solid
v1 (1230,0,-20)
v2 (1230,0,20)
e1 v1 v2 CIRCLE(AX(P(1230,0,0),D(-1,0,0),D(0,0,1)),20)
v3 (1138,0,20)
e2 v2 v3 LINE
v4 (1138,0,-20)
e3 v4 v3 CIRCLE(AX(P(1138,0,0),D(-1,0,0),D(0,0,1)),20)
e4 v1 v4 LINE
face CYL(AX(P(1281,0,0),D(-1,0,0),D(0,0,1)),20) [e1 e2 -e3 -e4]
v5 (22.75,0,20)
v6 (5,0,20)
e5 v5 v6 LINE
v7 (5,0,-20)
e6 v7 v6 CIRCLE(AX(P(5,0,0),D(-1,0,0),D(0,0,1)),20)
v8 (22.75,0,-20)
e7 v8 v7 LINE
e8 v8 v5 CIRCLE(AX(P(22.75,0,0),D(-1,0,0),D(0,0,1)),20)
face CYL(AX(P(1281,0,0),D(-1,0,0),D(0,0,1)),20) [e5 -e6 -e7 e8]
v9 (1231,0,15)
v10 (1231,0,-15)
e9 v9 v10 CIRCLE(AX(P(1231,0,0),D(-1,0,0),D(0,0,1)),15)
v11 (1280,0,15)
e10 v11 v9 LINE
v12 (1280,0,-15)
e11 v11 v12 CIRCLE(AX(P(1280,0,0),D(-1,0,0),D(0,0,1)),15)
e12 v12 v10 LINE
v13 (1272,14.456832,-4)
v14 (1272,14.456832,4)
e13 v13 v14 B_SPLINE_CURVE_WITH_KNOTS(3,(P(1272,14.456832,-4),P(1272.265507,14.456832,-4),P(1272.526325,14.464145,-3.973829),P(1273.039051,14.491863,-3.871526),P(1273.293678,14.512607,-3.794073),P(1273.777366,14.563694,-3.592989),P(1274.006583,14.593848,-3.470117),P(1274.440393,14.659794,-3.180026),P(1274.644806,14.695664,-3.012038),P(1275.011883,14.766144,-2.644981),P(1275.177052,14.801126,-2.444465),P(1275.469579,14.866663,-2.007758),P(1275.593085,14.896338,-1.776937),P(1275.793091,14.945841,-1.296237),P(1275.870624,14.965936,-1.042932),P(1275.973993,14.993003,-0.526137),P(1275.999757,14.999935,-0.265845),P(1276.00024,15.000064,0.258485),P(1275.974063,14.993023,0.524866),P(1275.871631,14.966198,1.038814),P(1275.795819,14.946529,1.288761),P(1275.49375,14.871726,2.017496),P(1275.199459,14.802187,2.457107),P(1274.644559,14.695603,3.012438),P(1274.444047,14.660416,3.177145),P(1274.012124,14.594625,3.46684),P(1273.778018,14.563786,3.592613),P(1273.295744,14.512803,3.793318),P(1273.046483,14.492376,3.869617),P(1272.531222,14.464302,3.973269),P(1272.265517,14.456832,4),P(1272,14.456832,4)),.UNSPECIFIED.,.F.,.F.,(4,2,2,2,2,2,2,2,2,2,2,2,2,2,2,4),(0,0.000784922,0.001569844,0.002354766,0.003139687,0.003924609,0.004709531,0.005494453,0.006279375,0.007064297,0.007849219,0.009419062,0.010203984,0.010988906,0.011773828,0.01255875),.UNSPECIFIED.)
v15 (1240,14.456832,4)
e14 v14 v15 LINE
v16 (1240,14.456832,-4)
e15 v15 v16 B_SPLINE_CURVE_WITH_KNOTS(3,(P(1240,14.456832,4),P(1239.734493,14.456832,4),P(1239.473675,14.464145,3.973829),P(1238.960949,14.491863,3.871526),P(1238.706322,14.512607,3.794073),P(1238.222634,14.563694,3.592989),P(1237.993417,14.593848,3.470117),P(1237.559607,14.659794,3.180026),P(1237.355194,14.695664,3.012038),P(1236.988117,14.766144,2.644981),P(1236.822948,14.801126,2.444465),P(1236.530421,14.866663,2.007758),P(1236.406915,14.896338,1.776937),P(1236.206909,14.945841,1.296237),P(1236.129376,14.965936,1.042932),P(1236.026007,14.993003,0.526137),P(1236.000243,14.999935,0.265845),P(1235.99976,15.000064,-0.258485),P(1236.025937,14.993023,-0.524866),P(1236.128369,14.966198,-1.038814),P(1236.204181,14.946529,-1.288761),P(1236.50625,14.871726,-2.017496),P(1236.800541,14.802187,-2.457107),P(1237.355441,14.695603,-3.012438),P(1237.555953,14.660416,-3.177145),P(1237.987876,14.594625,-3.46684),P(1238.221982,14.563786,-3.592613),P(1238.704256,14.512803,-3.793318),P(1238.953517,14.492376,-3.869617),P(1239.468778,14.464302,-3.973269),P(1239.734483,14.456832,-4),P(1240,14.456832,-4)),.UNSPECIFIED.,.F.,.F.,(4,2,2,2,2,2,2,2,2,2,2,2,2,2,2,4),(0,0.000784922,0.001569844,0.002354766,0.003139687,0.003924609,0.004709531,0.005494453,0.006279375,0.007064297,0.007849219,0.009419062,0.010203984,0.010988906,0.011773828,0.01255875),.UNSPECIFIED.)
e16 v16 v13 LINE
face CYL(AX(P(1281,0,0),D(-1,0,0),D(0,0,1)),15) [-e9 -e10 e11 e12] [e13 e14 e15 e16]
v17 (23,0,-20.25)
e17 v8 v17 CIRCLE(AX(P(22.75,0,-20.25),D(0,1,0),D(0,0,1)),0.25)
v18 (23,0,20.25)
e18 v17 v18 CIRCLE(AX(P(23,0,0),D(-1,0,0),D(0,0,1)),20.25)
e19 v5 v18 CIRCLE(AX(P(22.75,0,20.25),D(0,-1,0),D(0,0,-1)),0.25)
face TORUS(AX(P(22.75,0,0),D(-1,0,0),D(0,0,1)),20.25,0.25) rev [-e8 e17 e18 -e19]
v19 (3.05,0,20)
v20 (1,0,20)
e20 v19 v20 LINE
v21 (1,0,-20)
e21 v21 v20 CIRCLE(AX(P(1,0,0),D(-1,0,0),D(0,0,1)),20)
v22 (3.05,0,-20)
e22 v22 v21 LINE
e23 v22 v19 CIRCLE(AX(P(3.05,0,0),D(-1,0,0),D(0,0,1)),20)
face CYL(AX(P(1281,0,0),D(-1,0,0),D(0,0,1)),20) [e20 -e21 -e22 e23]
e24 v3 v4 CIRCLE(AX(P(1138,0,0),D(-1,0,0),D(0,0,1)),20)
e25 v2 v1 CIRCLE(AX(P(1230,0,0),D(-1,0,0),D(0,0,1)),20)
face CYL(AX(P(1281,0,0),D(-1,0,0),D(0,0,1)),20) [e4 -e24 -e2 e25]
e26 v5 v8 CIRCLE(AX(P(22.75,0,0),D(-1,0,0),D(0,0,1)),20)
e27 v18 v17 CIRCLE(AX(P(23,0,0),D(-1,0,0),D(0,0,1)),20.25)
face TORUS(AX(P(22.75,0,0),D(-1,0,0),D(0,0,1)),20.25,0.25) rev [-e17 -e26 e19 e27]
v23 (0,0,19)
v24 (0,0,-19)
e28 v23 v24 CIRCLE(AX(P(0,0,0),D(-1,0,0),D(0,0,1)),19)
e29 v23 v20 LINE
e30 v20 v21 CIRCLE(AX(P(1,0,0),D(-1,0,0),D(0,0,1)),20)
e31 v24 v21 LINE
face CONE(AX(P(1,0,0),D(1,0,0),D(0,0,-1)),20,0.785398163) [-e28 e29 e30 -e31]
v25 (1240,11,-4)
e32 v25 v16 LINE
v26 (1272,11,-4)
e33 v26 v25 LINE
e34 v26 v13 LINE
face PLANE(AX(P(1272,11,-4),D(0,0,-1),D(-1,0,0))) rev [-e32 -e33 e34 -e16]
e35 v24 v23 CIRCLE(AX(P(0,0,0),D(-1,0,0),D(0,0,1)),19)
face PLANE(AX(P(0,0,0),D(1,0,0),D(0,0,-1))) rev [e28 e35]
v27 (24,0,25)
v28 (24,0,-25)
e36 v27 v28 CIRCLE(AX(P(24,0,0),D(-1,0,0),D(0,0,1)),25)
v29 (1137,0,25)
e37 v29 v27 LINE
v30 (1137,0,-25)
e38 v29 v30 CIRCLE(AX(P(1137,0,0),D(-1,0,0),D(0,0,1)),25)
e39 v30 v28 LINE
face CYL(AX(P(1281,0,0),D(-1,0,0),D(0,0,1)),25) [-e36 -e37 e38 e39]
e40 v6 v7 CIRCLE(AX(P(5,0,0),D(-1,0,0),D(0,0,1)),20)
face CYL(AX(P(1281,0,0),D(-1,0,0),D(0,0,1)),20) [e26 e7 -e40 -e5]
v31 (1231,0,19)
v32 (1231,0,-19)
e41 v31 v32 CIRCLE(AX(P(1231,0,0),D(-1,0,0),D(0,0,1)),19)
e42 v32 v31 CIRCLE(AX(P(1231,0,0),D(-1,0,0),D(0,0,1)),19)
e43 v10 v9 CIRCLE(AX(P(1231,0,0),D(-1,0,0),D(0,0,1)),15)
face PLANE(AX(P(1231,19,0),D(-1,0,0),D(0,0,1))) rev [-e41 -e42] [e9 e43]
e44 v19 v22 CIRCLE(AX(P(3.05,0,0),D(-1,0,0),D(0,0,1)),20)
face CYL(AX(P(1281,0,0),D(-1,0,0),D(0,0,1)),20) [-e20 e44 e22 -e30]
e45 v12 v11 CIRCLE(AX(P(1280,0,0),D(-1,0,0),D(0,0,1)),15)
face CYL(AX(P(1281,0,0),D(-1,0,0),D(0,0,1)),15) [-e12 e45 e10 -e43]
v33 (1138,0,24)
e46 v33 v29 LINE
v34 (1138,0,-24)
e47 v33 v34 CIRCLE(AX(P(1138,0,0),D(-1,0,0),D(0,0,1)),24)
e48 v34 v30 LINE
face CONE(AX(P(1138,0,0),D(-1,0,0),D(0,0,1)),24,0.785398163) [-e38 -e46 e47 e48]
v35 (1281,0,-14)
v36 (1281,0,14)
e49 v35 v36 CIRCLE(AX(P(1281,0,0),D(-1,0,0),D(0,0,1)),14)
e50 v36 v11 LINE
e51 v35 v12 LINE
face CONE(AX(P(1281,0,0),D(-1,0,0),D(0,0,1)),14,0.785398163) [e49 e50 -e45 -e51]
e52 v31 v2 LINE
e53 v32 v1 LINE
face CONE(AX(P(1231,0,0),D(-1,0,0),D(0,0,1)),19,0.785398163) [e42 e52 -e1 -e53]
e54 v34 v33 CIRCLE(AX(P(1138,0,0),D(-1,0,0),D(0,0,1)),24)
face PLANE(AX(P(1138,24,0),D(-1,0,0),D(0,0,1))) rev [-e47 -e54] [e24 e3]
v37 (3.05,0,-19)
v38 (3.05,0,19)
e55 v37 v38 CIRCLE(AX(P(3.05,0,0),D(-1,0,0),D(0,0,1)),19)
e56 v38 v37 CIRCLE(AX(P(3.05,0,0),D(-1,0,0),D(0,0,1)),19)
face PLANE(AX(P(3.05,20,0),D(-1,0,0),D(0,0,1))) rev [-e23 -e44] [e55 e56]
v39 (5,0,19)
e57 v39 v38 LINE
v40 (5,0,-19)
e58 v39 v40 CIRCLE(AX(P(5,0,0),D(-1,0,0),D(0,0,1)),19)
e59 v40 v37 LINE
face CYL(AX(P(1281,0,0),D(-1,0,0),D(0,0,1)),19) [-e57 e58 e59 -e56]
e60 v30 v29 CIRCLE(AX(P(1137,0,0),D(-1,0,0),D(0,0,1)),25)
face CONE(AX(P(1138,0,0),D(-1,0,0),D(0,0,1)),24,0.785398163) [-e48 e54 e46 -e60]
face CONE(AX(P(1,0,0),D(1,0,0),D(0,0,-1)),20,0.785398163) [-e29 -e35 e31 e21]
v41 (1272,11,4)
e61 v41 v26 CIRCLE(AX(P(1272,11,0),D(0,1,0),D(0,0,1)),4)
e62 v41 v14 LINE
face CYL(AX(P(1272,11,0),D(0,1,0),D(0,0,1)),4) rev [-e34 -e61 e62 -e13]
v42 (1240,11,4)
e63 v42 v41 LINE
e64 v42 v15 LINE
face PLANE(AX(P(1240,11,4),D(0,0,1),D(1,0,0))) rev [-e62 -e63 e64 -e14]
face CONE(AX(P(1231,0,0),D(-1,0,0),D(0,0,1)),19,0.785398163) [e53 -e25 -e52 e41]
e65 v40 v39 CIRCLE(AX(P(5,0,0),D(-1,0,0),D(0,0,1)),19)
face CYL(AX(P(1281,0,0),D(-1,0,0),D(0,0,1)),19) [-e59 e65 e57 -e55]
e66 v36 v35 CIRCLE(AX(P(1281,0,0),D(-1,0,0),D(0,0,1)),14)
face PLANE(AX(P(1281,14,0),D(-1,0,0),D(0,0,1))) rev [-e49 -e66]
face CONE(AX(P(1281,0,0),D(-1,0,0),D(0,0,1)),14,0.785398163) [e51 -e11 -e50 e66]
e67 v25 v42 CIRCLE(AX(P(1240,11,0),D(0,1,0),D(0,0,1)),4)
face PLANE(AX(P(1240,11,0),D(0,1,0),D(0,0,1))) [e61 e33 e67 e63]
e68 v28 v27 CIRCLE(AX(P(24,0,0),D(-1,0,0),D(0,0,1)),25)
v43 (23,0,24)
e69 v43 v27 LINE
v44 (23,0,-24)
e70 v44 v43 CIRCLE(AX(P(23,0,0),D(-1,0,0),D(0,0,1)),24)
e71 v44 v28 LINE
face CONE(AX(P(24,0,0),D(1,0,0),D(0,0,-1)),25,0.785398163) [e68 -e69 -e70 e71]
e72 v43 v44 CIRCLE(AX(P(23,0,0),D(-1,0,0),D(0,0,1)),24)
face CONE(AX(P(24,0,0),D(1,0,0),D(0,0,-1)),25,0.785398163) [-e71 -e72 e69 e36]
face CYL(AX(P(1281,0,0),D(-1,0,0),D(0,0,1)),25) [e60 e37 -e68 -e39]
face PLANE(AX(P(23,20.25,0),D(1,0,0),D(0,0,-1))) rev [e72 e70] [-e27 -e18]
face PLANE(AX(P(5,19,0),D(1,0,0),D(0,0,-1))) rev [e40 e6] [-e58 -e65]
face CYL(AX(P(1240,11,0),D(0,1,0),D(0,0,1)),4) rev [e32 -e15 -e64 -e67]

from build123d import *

# Parameters (mm, degrees)
CUT_EXTRUDE_1_DEPTH = 4


with BuildPart() as part:
    # 草图1 → 旋转1 (revolve)
    with BuildSketch(Plane.XY, mode=Mode.PRIVATE) as revolve_1_sk:
        with BuildLine():
            Line((0, 0), (0, 19))
            Line((0, 19), (1, 20))
            Line((1, 20), (3.05, 20))
            Line((3.05, 20), (3.05, 19))
            Line((3.05, 19), (5, 19))
            Line((5, 19), (5, 20))
            Line((5, 20), (22.75, 20))
            ThreePointArc((22.75, 20), (22.926776695, 20.073223305), (23, 20.25))
            Line((23, 20.25), (23, 24))
            Line((23, 24), (24, 25))
            Line((24, 25), (1137, 25))
            Line((1137, 25), (1138, 24))
            Line((1138, 24), (1138, 20))
            Line((1138, 20), (1230, 20))
            Line((1230, 20), (1231, 19))
            Line((1231, 19), (1231, 15))
            Line((1231, 15), (1280, 15))
            Line((1280, 15), (1281, 14))
            Line((1281, 14), (1281, 0))
            Line((1281, 0), (0, 0))
        make_face()
    revolve(revolve_1_sk.sketch.rotate(Axis((1281, 0, 0), (-1, 0, 0)), 270), axis=Axis((1281, 0, 0), (-1, 0, 0)))

    # 草图2 → 切除-拉伸1 (cut)
    with BuildSketch(Plane(origin=(0, 15, 0), x_dir=(1, 0, 0), z_dir=(0, 1, 0))):
        with BuildLine():
            Line((1240, -4), (1272, -4))
            ThreePointArc((1272, -4), (1276, 0), (1272, 4))
            Line((1272, 4), (1240, 4))
            ThreePointArc((1240, 4), (1236, 0), (1240, -4))
        make_face()
    extrude(amount=-CUT_EXTRUDE_1_DEPTH, mode=Mode.SUBTRACT)


solid = part.part
